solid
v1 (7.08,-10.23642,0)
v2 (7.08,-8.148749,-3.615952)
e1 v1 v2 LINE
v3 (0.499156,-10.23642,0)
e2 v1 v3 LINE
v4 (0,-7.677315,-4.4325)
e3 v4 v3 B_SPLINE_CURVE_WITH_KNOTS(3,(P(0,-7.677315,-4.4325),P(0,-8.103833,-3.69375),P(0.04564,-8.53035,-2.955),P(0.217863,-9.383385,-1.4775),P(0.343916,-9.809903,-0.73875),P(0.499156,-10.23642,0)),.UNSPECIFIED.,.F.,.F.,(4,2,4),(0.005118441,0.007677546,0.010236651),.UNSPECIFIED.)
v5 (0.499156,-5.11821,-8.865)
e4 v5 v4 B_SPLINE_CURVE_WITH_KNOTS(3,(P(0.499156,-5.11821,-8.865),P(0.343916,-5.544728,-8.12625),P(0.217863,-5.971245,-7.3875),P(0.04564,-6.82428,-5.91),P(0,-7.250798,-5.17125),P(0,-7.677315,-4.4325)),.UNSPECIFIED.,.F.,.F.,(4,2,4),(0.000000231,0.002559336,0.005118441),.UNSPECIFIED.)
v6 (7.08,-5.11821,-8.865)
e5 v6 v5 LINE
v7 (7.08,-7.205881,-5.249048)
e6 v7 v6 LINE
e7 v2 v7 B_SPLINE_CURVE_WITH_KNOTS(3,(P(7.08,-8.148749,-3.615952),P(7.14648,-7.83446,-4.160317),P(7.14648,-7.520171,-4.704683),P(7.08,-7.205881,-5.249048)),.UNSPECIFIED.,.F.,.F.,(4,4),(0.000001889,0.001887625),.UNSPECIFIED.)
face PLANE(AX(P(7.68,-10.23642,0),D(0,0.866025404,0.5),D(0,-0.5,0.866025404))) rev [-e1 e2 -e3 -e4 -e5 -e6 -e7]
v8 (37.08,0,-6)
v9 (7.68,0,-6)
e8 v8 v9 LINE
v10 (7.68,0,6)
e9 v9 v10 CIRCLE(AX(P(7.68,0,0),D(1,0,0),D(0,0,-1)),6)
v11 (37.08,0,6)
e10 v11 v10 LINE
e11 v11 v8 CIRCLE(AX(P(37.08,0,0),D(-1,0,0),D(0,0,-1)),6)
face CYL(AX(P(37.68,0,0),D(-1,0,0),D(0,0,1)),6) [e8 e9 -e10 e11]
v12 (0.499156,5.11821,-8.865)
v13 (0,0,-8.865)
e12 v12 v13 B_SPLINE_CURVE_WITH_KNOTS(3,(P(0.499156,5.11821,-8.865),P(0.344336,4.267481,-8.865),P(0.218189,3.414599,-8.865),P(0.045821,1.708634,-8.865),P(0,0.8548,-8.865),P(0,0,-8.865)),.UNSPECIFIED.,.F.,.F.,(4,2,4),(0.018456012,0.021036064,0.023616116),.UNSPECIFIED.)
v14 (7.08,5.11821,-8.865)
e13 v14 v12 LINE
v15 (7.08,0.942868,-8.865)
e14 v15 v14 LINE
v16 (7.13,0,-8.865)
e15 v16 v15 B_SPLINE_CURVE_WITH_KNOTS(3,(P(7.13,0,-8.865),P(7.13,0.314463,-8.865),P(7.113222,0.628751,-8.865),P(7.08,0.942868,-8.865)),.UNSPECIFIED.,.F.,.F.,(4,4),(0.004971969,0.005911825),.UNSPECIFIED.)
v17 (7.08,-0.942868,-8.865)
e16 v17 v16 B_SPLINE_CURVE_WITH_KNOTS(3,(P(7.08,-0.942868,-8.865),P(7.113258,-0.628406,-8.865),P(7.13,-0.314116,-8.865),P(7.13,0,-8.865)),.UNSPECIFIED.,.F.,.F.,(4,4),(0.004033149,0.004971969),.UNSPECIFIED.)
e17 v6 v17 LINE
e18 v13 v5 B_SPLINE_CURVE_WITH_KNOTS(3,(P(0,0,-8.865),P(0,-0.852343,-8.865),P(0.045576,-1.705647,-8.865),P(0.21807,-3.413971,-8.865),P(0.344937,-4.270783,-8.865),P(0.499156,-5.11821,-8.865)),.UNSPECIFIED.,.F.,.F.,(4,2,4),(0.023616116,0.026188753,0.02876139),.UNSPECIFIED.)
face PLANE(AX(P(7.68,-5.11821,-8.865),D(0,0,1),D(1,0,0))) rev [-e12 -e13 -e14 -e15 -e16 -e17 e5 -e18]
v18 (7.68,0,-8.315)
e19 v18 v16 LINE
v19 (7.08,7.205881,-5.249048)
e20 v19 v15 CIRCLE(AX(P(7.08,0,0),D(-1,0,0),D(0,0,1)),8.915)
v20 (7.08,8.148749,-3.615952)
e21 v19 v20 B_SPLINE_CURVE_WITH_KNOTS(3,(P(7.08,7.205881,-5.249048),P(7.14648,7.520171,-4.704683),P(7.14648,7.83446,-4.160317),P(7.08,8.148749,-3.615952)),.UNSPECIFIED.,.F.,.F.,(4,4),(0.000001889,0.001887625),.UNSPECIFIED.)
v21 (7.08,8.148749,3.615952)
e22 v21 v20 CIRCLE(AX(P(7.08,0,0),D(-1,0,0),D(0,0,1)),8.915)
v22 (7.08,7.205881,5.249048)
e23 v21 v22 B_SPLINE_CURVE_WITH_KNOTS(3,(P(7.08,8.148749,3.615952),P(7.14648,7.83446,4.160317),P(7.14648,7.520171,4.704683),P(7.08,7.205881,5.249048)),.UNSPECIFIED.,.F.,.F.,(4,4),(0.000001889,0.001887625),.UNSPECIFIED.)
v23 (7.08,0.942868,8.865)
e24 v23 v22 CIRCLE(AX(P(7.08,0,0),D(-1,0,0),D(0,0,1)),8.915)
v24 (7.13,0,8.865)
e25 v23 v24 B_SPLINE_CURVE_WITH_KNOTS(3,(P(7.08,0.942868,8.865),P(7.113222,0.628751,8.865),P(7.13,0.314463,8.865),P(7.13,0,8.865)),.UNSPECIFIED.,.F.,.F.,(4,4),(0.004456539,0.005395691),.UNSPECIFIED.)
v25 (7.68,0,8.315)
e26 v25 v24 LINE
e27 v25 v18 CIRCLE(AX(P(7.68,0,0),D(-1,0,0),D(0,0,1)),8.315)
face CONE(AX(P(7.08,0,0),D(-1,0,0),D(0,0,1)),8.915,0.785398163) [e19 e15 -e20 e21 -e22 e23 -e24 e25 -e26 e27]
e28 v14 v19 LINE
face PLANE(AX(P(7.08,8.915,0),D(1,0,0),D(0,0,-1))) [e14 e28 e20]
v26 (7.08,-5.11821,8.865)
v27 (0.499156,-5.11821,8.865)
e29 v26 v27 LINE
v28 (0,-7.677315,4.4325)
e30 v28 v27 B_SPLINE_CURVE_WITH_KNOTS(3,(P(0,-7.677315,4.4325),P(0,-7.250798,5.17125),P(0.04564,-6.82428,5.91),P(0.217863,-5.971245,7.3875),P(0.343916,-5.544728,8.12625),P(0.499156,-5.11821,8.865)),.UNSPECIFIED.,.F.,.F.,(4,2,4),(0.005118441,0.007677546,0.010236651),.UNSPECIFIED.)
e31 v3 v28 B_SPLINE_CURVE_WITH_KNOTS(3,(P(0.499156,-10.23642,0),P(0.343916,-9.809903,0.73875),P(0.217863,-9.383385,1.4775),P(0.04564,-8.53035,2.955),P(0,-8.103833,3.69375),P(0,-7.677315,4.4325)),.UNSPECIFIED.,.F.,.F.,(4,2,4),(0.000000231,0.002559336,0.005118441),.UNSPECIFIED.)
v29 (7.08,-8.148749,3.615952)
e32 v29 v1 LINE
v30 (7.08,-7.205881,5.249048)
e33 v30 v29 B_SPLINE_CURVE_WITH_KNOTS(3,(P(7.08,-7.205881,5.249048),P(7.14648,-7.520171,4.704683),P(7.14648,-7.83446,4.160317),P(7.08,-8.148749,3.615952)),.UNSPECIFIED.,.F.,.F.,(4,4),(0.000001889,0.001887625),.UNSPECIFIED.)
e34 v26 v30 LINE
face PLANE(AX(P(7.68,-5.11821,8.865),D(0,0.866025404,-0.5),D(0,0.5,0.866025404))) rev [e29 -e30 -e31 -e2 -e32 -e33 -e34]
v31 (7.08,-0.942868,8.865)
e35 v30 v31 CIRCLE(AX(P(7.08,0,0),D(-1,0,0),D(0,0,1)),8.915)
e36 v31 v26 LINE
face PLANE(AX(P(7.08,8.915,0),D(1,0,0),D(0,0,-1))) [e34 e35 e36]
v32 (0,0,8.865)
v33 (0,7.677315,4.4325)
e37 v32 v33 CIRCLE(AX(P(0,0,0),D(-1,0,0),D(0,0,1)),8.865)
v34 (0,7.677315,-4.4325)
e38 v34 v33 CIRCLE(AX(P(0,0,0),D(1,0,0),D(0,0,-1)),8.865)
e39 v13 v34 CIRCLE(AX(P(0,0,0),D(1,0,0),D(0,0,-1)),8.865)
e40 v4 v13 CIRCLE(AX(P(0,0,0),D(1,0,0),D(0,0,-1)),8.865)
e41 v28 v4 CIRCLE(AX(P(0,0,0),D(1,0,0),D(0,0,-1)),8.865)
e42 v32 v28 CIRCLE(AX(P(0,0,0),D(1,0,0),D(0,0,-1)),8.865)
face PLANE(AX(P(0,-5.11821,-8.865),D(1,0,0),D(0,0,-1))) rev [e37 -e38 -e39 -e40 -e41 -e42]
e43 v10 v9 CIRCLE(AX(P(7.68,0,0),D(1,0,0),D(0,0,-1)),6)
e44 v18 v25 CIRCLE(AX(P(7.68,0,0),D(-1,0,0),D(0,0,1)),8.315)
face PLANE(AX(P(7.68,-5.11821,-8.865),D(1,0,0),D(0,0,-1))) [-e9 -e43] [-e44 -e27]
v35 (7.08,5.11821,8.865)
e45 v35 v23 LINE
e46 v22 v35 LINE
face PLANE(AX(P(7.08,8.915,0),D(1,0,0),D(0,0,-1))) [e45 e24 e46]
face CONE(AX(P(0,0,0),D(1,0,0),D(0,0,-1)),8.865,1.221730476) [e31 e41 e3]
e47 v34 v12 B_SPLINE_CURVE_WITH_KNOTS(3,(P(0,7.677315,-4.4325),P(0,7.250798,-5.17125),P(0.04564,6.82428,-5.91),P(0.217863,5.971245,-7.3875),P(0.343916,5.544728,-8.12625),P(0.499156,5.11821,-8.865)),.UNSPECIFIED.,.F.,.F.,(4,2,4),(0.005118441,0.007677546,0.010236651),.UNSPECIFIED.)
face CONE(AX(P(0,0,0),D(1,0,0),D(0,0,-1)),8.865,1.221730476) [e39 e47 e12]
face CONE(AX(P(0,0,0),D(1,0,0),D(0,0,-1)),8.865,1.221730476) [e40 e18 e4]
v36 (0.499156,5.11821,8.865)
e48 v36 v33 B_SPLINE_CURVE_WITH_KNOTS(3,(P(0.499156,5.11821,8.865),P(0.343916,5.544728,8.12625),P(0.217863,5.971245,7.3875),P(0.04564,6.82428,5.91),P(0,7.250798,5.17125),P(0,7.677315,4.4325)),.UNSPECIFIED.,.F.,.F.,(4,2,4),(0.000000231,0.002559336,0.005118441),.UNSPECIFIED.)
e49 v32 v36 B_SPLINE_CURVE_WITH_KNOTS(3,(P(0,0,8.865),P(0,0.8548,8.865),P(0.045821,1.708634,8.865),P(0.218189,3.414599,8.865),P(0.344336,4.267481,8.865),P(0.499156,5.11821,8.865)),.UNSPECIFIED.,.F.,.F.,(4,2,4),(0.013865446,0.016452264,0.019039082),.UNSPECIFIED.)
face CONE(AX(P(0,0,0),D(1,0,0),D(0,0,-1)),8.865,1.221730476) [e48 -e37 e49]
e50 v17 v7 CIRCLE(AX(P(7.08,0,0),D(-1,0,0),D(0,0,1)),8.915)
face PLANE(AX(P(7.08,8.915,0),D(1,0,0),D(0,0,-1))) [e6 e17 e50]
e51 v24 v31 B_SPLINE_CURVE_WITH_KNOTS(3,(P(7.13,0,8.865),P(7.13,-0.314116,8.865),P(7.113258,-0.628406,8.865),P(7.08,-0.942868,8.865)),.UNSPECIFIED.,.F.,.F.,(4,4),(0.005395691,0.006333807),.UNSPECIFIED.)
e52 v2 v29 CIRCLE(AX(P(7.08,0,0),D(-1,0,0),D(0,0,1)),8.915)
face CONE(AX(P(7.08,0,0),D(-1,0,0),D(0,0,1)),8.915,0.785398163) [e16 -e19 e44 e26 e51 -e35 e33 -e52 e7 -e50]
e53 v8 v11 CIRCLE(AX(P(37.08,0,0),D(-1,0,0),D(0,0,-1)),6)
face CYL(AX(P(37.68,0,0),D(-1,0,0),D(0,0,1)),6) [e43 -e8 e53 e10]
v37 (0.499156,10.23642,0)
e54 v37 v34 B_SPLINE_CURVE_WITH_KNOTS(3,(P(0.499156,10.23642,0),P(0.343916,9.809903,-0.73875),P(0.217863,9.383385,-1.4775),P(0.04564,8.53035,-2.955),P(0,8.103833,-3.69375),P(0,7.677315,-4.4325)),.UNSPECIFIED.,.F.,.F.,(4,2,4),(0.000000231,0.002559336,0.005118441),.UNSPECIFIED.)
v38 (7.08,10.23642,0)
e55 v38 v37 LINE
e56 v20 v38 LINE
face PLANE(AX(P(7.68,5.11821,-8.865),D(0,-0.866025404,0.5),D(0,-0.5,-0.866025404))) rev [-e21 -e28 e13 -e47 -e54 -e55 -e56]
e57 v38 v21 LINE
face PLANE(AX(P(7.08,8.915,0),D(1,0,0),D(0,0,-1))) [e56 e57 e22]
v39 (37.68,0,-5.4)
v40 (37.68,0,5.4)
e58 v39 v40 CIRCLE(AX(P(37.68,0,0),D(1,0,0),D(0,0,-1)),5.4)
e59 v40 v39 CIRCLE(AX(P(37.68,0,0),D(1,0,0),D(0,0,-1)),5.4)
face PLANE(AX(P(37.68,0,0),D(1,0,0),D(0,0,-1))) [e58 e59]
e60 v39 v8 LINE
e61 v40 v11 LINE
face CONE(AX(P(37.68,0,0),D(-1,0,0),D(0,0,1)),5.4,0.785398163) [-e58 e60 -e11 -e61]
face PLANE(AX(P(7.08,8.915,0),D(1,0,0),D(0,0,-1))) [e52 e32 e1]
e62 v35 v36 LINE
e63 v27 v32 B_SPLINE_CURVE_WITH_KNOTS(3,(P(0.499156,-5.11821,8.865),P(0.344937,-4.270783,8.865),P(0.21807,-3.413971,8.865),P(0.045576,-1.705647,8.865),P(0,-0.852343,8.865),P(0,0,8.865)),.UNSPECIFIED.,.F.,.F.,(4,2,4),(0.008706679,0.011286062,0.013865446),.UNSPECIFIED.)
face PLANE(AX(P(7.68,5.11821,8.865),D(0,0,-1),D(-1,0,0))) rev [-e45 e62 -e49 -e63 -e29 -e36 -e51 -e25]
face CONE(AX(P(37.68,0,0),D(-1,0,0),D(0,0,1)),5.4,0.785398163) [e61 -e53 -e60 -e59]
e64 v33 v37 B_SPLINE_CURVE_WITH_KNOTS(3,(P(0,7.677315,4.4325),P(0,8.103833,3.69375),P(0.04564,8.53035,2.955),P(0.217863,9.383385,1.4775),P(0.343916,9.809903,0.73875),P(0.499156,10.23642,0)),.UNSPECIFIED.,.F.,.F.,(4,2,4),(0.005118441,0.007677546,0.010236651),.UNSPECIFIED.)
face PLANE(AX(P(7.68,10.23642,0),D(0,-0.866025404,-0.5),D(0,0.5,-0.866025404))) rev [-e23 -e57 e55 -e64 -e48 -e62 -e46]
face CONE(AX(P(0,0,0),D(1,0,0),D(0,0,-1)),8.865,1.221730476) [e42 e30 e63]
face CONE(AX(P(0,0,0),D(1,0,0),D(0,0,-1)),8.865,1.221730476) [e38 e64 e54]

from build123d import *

# Parameters (mm, degrees)
BASEHEAD_DEPTH = 7.68
SKETCH5_R      = 6
BASEBODY_DEPTH = 30
CHAMFER1_SIZE  = 0.6


with BuildPart() as part:
    # Sketch2 → BaseHead (new body)
    with BuildSketch(Plane(origin=(0, 0, 0), x_dir=(0, 0, -1), z_dir=(1, 0, 0))):
        Polygon((8.865, -5.118210136), (8.865, 5.118210136), (0, 10.236420273), (-8.865, 5.118210136), (-8.865, -5.118210136), (0, -10.236420273), align=None)
    extrude(amount=BASEHEAD_DEPTH)

    # Sketch3 → BearingFace (revolve, cut)
    with BuildSketch(Plane.XY, mode=Mode.PRIVATE) as bearingface_sk:
        Polygon((7.68, 10.236420273), (7.68, 8.315), (7.08, 8.915), (7.08, 10.236420273), align=None)
    revolve(bearingface_sk.sketch.rotate(Axis((-0.957090588, 0, 0), (1, 0, 0)), 90), axis=Axis((-0.957090588, 0, 0), (1, 0, 0)), mode=Mode.SUBTRACT)

    # Sketch4 → HeadChamfer (revolve, cut)
    with BuildSketch(Plane.XY):
        Polygon((0, 10.236420273), (0.499156158, 10.236420273), (0, 8.865), align=None)
    revolve(axis=Axis((-0.493528746, 0, 0), (1, 0, 0)), mode=Mode.SUBTRACT)

    # Sketch5 → BaseBody (add)
    with BuildSketch(Plane(origin=(7.68, 0, 0), x_dir=(0, 0, -1), z_dir=(1, 0, 0))):
        Circle(SKETCH5_R)
    extrude(amount=BASEBODY_DEPTH)

    # Chamfer1
    chamfer1_edges = [part.edges().sort_by_distance(p)[0] for p in [
        (37.68, 0, 6),
    ]]
    chamfer(chamfer1_edges, length=CHAMFER1_SIZE)


solid = part.part
